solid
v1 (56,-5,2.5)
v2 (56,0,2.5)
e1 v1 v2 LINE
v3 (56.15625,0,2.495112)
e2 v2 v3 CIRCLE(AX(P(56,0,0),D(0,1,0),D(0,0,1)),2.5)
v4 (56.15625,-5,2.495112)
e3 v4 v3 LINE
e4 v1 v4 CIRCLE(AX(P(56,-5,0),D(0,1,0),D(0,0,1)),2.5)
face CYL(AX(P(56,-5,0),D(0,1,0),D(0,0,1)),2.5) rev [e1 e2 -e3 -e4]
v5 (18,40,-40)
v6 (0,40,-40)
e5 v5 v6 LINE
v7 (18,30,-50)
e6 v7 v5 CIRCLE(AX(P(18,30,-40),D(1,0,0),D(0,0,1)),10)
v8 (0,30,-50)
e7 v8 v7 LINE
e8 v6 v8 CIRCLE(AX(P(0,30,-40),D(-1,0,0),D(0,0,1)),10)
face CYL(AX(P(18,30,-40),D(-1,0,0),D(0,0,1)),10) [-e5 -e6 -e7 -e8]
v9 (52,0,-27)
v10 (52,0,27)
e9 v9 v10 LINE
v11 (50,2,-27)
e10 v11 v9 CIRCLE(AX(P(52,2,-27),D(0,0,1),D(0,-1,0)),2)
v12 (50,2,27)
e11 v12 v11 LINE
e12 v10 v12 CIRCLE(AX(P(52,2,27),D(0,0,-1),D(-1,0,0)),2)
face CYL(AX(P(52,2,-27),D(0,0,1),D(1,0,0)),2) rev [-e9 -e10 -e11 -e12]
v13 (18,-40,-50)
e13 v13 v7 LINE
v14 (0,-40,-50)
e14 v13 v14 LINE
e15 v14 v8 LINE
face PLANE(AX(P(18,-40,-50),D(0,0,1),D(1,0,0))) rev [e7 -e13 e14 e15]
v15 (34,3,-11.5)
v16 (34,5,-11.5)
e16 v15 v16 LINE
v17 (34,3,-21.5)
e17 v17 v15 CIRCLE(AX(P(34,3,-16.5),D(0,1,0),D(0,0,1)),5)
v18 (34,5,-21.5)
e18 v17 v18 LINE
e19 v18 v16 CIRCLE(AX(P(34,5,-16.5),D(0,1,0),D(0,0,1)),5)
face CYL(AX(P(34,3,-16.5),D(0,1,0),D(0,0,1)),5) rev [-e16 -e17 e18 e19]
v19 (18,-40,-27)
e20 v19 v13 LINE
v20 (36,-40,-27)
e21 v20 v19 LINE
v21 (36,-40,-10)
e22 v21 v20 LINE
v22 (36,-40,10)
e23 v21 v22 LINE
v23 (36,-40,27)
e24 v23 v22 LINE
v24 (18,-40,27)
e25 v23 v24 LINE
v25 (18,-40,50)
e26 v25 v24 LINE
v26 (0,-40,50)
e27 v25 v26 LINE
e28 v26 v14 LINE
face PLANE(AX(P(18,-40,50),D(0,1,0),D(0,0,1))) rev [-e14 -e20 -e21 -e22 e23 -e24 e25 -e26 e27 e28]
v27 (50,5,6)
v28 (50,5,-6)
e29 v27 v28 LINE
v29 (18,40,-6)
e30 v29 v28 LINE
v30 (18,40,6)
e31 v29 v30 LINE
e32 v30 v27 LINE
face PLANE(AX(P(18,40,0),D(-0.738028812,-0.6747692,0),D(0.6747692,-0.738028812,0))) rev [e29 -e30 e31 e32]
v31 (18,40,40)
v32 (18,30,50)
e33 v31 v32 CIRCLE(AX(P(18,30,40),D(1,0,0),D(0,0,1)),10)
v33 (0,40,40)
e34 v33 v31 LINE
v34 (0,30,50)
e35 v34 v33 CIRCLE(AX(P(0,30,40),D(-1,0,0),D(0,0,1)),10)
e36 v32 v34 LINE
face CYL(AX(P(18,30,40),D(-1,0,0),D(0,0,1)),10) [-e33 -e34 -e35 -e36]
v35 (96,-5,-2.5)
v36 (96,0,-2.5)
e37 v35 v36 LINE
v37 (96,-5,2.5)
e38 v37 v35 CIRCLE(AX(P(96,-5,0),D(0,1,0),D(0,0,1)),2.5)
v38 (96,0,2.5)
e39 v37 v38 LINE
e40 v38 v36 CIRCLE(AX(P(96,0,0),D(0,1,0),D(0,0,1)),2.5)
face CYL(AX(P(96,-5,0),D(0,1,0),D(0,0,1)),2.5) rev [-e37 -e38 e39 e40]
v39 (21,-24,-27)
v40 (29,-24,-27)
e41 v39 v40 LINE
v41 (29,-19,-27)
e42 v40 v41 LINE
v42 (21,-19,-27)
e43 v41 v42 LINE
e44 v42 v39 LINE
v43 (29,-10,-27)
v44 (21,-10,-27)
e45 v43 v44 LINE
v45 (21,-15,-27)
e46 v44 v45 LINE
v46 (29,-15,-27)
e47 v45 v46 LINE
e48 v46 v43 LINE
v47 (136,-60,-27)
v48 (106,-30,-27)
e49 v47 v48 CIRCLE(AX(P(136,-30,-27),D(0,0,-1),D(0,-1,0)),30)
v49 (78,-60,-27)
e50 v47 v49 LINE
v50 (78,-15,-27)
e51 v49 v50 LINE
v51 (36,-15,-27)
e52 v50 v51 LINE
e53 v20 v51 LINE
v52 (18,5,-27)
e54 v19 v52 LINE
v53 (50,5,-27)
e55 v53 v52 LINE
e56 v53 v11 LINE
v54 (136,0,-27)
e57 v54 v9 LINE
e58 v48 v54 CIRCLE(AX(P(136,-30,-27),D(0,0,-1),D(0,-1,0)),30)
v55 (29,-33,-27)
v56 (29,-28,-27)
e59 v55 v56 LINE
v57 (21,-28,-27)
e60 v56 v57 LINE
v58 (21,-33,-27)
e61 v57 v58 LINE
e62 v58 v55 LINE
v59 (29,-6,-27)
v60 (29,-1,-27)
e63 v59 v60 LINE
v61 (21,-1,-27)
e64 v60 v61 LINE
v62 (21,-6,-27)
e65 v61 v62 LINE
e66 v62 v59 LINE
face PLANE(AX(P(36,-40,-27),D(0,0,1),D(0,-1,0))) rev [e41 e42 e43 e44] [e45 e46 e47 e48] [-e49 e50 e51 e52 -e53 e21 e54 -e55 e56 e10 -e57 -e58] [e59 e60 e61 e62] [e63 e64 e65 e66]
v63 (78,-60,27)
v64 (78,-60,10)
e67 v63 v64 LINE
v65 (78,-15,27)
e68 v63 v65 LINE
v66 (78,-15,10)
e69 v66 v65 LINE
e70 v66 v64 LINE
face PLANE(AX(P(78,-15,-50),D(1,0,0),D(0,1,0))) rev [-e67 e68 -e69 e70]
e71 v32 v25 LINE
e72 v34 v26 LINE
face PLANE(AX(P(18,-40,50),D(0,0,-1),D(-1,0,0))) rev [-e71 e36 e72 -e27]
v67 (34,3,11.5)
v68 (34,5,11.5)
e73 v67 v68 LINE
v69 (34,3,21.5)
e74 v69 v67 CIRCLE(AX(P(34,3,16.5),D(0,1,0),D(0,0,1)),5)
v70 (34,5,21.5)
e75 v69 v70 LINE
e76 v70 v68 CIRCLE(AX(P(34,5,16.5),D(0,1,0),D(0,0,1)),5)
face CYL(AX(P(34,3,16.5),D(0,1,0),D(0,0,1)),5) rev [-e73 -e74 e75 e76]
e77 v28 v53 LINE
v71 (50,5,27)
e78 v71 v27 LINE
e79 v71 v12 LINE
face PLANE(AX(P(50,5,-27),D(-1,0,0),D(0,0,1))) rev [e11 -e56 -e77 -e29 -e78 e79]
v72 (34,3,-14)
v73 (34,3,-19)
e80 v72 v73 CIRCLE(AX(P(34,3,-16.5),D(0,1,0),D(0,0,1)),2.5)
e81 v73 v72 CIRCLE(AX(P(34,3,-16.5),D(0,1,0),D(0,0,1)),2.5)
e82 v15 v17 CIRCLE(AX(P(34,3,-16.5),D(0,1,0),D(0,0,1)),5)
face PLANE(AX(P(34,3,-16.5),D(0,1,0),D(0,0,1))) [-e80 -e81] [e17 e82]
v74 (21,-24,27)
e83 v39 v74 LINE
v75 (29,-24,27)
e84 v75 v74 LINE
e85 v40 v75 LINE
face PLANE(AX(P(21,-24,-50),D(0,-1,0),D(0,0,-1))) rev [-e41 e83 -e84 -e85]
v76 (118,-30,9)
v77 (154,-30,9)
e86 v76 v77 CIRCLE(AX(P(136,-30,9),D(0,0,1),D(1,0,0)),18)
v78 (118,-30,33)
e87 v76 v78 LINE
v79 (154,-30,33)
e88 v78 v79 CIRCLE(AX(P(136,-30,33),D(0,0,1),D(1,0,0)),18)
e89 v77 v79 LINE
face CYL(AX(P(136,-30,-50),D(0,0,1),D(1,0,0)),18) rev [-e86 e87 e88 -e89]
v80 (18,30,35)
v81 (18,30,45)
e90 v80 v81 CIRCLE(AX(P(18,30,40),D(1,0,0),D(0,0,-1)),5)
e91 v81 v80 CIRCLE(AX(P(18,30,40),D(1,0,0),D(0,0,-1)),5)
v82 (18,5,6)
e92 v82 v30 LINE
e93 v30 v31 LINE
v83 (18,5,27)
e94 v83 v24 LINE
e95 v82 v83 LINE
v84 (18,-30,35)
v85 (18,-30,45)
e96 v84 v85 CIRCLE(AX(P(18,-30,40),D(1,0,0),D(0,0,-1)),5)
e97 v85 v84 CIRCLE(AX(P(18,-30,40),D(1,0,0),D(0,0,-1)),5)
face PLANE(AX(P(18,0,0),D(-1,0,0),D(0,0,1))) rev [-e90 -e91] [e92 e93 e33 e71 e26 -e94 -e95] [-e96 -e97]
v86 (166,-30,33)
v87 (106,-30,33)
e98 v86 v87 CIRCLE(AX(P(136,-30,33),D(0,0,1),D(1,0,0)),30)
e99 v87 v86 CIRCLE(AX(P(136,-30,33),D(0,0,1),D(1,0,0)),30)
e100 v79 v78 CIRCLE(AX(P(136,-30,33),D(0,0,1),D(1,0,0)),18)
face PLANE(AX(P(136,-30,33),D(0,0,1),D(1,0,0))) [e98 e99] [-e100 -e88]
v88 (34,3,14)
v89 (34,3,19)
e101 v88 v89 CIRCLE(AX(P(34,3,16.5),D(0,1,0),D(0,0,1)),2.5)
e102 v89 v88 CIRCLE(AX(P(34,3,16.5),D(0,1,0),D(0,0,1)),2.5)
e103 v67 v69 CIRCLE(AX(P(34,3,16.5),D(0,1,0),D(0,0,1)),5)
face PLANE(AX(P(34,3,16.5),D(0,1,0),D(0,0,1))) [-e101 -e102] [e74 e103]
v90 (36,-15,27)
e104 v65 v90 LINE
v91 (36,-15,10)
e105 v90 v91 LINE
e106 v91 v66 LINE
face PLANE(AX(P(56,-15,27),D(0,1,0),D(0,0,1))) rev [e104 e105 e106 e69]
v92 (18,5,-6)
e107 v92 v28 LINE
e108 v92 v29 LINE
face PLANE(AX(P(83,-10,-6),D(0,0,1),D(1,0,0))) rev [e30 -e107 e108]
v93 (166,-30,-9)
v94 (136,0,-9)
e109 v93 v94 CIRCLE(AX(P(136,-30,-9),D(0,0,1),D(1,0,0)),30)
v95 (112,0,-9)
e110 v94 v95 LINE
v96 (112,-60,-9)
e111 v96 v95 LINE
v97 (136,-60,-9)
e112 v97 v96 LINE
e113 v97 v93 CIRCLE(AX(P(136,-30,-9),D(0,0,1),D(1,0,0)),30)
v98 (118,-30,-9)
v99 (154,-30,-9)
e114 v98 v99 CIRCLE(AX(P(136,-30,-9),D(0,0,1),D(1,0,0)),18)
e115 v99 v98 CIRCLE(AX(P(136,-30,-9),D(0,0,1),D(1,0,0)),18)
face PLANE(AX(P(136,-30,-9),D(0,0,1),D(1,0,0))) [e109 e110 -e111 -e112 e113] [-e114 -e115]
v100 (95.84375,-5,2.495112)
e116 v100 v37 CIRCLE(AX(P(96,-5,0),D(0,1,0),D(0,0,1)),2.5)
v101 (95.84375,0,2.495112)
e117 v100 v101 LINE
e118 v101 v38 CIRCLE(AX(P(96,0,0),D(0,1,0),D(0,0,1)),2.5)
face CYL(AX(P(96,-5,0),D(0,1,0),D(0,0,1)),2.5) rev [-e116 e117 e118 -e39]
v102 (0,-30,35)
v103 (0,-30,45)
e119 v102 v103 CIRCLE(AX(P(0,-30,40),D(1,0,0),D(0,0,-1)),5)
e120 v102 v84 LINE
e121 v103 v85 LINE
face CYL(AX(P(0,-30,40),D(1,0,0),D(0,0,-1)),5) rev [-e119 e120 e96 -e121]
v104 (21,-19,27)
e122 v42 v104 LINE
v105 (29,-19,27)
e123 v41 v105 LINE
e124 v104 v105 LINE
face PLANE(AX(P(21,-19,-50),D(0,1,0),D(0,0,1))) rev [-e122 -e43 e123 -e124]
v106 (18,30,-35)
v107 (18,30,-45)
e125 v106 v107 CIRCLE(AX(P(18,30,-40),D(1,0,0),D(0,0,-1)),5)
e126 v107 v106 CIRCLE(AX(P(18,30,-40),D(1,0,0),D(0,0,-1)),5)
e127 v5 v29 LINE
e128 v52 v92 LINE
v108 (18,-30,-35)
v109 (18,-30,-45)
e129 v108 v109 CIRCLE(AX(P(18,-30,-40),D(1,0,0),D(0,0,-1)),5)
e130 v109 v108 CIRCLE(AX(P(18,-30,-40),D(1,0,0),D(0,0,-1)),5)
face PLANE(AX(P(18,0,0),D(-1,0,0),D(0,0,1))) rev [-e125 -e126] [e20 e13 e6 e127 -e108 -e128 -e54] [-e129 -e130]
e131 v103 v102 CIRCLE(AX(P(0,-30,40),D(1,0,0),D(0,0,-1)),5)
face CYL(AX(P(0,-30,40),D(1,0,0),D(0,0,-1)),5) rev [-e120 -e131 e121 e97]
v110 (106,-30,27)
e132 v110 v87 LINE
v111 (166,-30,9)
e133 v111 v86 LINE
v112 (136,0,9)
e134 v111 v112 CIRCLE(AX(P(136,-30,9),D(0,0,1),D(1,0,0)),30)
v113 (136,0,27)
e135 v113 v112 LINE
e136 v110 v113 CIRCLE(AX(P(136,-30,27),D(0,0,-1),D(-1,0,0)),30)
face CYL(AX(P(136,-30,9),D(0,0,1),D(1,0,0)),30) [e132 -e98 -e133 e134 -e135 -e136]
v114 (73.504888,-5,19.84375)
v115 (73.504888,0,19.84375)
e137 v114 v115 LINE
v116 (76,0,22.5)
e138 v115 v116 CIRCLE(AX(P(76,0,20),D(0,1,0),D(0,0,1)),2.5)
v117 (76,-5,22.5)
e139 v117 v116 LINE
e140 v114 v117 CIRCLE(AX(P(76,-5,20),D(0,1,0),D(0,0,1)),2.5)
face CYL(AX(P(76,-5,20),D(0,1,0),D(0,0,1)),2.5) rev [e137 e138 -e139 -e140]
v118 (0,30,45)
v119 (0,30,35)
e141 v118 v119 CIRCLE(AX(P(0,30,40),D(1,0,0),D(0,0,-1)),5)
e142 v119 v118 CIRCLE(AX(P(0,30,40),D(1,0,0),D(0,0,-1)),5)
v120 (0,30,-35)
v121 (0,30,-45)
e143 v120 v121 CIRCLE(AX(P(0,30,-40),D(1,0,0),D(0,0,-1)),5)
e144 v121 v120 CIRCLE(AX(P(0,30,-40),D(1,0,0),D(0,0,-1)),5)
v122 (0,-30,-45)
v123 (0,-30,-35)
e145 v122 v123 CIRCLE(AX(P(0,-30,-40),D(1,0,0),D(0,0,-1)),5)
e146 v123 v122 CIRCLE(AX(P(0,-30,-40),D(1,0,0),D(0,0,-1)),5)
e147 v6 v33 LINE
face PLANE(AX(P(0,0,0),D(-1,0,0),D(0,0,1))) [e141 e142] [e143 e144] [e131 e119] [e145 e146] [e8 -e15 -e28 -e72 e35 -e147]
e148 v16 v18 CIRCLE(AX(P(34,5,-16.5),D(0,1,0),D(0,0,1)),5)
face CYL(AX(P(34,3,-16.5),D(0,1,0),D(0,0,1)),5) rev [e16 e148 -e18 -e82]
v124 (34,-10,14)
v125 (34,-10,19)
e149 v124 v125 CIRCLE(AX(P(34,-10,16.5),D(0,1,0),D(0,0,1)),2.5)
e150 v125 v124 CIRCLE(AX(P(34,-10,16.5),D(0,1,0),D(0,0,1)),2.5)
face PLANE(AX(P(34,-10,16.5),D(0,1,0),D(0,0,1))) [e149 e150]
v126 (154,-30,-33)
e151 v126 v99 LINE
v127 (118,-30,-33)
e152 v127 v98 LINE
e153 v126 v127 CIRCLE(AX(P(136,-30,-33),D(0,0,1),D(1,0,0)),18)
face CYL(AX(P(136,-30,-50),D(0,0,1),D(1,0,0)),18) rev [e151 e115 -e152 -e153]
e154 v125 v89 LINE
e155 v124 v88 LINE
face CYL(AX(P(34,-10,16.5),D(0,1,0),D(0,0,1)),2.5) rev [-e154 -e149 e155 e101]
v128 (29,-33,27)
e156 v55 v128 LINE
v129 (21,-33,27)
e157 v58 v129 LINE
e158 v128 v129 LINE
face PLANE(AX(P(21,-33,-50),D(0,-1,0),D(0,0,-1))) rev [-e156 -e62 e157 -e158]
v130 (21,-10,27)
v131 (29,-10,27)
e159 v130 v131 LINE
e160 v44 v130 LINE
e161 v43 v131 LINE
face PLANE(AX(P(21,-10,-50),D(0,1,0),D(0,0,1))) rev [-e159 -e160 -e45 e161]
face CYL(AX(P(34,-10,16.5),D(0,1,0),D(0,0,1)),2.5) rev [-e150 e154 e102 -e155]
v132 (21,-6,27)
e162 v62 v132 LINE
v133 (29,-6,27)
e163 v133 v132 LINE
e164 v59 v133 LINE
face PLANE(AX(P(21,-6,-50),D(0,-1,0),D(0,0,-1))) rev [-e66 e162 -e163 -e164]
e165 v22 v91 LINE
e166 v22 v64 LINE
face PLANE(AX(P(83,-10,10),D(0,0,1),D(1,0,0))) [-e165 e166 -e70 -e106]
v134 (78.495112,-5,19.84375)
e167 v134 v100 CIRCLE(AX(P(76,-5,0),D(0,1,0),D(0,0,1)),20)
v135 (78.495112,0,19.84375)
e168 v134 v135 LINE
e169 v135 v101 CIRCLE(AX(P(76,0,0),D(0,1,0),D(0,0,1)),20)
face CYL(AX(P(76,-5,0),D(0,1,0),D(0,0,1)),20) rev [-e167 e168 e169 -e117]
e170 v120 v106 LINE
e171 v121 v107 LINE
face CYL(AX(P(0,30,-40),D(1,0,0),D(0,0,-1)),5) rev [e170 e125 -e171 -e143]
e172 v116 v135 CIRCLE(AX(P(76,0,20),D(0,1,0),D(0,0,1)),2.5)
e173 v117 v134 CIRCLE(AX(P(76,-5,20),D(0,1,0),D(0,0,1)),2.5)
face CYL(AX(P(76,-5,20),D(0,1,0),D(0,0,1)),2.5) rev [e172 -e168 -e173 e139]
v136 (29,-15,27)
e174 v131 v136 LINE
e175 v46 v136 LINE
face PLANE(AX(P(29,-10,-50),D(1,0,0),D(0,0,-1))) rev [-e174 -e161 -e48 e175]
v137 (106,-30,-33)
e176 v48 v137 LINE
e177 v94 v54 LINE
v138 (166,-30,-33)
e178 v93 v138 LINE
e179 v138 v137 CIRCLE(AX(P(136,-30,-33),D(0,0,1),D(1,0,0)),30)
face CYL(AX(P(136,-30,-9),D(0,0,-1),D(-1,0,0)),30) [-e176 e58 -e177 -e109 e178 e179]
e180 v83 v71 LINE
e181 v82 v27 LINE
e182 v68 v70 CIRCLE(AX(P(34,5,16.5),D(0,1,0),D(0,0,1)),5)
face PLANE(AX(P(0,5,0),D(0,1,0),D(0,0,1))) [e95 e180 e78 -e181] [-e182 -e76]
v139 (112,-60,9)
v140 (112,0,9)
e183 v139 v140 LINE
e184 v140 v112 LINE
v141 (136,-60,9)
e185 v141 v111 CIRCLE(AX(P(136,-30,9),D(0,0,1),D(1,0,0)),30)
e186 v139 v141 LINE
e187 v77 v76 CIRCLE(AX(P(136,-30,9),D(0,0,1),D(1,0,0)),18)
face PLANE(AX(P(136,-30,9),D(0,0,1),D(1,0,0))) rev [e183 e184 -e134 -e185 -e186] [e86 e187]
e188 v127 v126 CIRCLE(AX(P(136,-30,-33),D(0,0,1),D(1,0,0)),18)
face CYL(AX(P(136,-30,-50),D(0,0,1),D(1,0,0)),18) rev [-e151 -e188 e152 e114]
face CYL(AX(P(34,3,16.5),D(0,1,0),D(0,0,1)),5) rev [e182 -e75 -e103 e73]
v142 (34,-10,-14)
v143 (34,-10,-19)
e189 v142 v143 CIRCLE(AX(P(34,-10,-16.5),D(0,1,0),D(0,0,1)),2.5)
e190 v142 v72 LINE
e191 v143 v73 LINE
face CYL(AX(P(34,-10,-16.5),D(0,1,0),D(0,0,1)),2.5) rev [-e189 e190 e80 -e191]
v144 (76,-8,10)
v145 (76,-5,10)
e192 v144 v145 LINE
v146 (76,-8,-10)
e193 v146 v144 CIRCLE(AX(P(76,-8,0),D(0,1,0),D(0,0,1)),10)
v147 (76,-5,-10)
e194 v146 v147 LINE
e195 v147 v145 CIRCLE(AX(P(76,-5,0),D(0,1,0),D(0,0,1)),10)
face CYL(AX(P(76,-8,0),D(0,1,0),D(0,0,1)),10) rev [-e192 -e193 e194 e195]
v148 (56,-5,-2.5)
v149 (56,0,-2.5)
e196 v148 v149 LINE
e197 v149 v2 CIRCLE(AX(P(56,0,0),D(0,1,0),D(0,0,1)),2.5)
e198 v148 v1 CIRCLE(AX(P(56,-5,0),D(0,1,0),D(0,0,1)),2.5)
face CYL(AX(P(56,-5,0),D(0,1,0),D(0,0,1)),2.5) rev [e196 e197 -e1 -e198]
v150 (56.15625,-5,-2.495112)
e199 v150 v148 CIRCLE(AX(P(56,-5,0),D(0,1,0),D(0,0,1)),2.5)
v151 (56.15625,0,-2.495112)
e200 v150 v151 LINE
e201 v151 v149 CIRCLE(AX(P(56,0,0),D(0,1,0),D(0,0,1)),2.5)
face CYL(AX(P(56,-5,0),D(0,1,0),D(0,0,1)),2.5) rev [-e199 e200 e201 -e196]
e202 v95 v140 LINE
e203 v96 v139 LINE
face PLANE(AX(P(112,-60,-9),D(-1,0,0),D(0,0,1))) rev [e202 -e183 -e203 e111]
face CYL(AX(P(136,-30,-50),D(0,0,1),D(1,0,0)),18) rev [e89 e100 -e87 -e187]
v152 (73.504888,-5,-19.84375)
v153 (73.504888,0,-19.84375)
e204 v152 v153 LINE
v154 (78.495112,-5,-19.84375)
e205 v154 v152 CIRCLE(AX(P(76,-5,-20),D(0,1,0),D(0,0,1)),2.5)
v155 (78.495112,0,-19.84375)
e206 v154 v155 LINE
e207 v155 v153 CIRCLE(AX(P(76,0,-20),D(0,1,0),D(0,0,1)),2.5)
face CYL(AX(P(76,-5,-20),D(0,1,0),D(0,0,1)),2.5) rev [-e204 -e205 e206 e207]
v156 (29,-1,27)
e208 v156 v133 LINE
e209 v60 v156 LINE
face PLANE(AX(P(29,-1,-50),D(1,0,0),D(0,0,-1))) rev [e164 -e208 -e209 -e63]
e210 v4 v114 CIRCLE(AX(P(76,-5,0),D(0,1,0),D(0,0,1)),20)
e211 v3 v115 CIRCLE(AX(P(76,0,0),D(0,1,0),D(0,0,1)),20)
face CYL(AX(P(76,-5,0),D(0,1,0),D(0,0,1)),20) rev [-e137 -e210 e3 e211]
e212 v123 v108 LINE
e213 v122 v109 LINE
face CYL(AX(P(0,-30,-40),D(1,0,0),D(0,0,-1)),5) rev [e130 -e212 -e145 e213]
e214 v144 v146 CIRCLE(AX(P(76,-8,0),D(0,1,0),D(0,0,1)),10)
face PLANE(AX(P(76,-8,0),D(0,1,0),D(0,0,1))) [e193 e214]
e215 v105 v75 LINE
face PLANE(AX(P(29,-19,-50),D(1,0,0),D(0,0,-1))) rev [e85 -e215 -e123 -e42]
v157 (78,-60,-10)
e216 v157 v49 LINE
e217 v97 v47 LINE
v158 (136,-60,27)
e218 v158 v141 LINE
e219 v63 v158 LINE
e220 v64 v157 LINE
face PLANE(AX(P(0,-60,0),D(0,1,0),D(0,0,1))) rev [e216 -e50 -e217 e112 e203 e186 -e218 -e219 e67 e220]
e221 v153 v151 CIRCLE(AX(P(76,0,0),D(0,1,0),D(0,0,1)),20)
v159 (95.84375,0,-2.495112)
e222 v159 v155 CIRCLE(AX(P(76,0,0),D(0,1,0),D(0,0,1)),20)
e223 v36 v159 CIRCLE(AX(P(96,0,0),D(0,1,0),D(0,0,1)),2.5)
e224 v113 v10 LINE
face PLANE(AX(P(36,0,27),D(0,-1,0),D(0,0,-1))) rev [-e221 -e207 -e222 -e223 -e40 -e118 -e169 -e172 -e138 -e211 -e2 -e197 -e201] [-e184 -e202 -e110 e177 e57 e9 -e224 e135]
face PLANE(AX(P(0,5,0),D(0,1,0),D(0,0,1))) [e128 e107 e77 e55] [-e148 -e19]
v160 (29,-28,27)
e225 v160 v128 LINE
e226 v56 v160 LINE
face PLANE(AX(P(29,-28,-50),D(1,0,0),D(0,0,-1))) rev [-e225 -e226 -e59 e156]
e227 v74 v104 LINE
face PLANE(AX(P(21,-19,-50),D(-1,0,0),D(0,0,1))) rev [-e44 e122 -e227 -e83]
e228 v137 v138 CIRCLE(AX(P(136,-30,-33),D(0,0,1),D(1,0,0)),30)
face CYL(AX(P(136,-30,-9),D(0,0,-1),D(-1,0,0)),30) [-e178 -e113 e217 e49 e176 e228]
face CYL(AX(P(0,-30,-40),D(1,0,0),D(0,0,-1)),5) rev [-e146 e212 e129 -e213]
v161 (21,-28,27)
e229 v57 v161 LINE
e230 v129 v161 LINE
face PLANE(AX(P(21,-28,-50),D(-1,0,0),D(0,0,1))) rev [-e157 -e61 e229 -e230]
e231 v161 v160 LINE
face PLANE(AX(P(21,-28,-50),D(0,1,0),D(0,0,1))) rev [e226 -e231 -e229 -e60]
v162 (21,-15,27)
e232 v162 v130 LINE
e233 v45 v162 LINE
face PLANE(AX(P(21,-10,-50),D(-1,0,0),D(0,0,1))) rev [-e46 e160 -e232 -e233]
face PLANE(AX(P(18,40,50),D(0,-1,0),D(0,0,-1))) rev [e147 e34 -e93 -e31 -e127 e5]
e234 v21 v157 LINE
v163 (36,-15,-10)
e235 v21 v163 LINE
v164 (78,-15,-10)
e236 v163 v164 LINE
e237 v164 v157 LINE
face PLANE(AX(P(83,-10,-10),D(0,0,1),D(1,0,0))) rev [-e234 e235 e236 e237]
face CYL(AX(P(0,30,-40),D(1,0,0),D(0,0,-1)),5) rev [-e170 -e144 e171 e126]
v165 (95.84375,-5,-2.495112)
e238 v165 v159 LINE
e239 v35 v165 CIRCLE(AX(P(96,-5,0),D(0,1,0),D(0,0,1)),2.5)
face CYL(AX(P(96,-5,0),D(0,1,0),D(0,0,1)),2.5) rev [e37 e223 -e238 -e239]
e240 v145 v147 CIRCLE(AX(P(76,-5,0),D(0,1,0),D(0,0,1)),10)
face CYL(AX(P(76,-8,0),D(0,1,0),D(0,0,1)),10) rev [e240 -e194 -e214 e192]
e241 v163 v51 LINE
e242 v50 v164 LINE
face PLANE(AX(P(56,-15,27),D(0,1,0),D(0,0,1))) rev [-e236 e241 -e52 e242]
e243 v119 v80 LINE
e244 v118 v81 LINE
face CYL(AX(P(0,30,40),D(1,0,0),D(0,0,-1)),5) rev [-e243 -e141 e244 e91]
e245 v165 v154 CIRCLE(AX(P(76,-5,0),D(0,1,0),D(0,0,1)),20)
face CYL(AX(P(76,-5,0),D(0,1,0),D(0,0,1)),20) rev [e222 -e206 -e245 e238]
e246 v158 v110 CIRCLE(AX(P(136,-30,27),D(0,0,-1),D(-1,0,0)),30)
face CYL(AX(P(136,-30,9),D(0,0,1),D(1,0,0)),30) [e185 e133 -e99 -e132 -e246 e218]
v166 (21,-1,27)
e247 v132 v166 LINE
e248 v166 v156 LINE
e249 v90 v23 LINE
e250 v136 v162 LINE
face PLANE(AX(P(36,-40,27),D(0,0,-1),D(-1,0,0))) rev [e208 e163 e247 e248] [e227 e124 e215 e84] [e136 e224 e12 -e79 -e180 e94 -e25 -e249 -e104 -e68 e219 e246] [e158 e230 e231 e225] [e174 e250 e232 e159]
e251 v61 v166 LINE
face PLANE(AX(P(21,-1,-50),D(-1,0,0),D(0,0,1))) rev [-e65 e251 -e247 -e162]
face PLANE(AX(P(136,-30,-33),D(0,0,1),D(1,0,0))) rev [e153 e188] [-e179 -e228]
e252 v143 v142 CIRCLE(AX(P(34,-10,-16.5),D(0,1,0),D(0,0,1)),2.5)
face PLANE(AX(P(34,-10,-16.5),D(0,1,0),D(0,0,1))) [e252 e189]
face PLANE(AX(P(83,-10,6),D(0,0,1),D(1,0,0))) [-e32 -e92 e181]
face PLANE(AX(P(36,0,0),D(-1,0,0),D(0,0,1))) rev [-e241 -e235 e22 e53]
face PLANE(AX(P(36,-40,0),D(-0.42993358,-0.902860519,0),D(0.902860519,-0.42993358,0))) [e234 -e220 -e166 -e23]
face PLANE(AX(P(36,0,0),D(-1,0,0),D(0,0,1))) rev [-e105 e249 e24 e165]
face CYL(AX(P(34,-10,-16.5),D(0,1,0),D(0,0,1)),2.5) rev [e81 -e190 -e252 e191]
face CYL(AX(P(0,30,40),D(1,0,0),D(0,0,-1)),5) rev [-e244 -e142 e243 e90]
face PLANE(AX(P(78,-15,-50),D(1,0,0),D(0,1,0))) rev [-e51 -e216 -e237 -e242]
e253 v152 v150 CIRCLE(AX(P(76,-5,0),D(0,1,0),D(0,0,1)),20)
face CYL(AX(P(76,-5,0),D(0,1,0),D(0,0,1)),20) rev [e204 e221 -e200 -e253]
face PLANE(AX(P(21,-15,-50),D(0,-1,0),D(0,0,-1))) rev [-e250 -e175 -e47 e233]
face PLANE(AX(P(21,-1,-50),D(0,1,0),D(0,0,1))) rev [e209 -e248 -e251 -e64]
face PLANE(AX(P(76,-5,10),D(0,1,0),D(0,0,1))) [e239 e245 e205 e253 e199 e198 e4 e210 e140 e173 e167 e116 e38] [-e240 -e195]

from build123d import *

# Parameters (mm, degrees)
MOUNTING_FLANGE_SKETCH_W          = 100
MOUNTING_FLANGE_SKETCH_H          = 80
MOUNTING_FLANGE_DEPTH             = 18
FLANGE_BOSS_BLOCK_SKETCH_W        = 54
FLANGE_BOSS_BLOCK_SKETCH_H        = 40
FLANGE_BOSS_BLOCK_DEPTH           = 18
ARM_RISER_SKETCH_W                = 54
ARM_RISER_SKETCH_H                = 15
ARM_RISER_DEPTH                   = 20
SUPPORT_ARM_SKETCH_W              = 80
SUPPORT_ARM_SKETCH_H              = 54
SUPPORT_ARM_DEPTH                 = 60
CLEVIS_LUG_1_SKETCH_R             = 30
CLEVIS_LUG_1_DEPTH                = 24
CLEVIS_START                      = 24
CLEVIS_LUG_2_SKETCH_R             = 30
CLEVIS_LUG_2_DEPTH                = 24
CLEVIS_BORE_SKETCH_R              = 18
CLEVIS_BORE_36_DEPTH              = 196.05127531
CLEVIS_SLOT_SKETCH_W              = 24
CLEVIS_SLOT_SKETCH_H              = 18
CLEVIS_SLOT_24_MM_DEPTH           = 184.455716727
ARM_RELIEF_CUT_SKETCH_W           = 22
ARM_RELIEF_CUT_SKETCH_H           = 45
ARM_RELIEF_CUT_DEPTH              = 193.574660846
ARM_RIB_20_MM_REACH               = 185.456
ARM_RIB_SKETCH_WALL_W             = 415.430246854
ARM_RIB_SKETCH_WALL_H             = 20
TOP_PAD_SKETCH_W                  = 32
TOP_PAD_SKETCH_H                  = 54
TOP_PAD_DEPTH                     = 5
TOP_PAD_FILLET_R2_R               = 2
GUSSET_RIB_12_MM_REACH            = 185.456
GUSSET_RIB_SKETCH_WALL_W          = 416.33505626
GUSSET_RIB_SKETCH_WALL_H          = 12
FLANGE_CORNER_FILLETS_R10_R       = 10
FLANGE_MOUNTING_HOLES_SKETCH_R    = 5
FLANGE_MOUNTING_HOLES_4X_DEPTH    = 168.343957166
SIDE_SQUARE_POCKETS_4X_DEPTH      = 193.574660846
SIDE_SQUARE_POCKETS_4X_DEPTH_BACK = 193.574660846
SIDE_SQUARE_POCKETS_SKETCH_W      = 8
SIDE_SQUARE_POCKETS_SKETCH_H      = 5
COUNTERBORE_SKETCH_R              = 5
COUNTERBORES_10_DEPTH             = 2
PILOT_HOLES_SKETCH_R              = 2.5
PILOT_HOLES_5_DEPTH               = 13
ARM_TOP_RECESS_40_DEPTH           = 5
RECESS_CENTRE_POCKET_SKETCH_R     = 10
RECESS_CENTRE_POCKET_20_DEPTH     = 3


with BuildPart() as part:
    # Mounting Flange Sketch → Mounting Flange (new body)
    with BuildSketch(Plane(origin=(0, 0, 0), x_dir=(0, 0, -1), z_dir=(1, 0, 0))):
        Rectangle(MOUNTING_FLANGE_SKETCH_W, MOUNTING_FLANGE_SKETCH_H)
    extrude(amount=MOUNTING_FLANGE_DEPTH)

    # Flange Boss Block Sketch → Flange Boss Block (add)
    with BuildSketch(Plane(origin=(18, 0, 0), x_dir=(0, 0, -1), z_dir=(1, 0, 0))):
        with Locations((0, -20)):
            Rectangle(FLANGE_BOSS_BLOCK_SKETCH_W, FLANGE_BOSS_BLOCK_SKETCH_H)
    extrude(amount=FLANGE_BOSS_BLOCK_DEPTH)

    # Arm Riser Sketch → Arm Riser (add)
    with BuildSketch(Plane(origin=(36, 0, 0), x_dir=(0, 0, -1), z_dir=(1, 0, 0))):
        with Locations((0, -7.5)):
            Rectangle(ARM_RISER_SKETCH_W, ARM_RISER_SKETCH_H)
    extrude(amount=ARM_RISER_DEPTH)

    # Support Arm Sketch → Support Arm (add)
    with BuildSketch(Plane(origin=(0, 0, 0), x_dir=(1, 0, 0), z_dir=(0, 1, 0))):
        with Locations((96, 0)):
            Rectangle(SUPPORT_ARM_SKETCH_W, SUPPORT_ARM_SKETCH_H)
    extrude(amount=-SUPPORT_ARM_DEPTH)

    # Clevis Lug 1 Sketch → Clevis Lug 1 (add)
    with BuildSketch(Plane.XY.offset(33)):
        with Locations((136, -30)):
            Circle(CLEVIS_LUG_1_SKETCH_R)
    extrude(amount=-CLEVIS_LUG_1_DEPTH)

    # Clevis Lug 2 Sketch → Clevis Lug 2 (add)
    with BuildSketch(Plane.XY.offset(-33).offset(CLEVIS_START)):
        with Locations((136, -30)):
            Circle(CLEVIS_LUG_2_SKETCH_R)
    extrude(amount=-CLEVIS_LUG_2_DEPTH)

    # Clevis Bore Sketch → Clevis Bore Ø36 (cut, through all)
    with BuildSketch(Plane.XY.offset(33)):
        with Locations((136, -30)):
            Circle(CLEVIS_BORE_SKETCH_R)
    extrude(amount=-CLEVIS_BORE_36_DEPTH, mode=Mode.SUBTRACT)

    # Clevis Slot Sketch → Clevis Slot 24 mm (cut, through all)
    with BuildSketch(Plane(origin=(0, 0, 0), x_dir=(1, 0, 0), z_dir=(0, 1, 0))):
        with Locations((124, 0)):
            Rectangle(CLEVIS_SLOT_SKETCH_W, CLEVIS_SLOT_SKETCH_H)
    extrude(amount=-CLEVIS_SLOT_24_MM_DEPTH, mode=Mode.SUBTRACT)

    # Arm Relief Cut Sketch → Arm Relief Cut (cut, through all)
    with BuildSketch(Plane.XY.offset(27)):
        with Locations((67, -37.5)):
            Rectangle(ARM_RELIEF_CUT_SKETCH_W, ARM_RELIEF_CUT_SKETCH_H)
    extrude(amount=-ARM_RELIEF_CUT_DEPTH, mode=Mode.SUBTRACT)

    # Arm Rib Sketch wall → Arm Rib 20 mm (add, up to next)
    with BuildSketch(Plane(origin=(57, -50, 0), x_dir=(0.902860518824, -0.429933580392, 0), z_dir=(0.429933580392, 0.902860518824, 0)), mode=Mode.PRIVATE) as arm_rib_20_mm_sk1:
        Rectangle(ARM_RIB_SKETCH_WALL_W, ARM_RIB_SKETCH_WALL_H)
    arm_rib_20_mm_tool1 = extrude(arm_rib_20_mm_sk1.sketch, amount=ARM_RIB_20_MM_REACH, mode=Mode.PRIVATE) - part.part
    add(arm_rib_20_mm_tool1.solids().sort_by_distance((57, -50, 0))[0])

    # Top Pad Sketch → Top Pad (add)
    with BuildSketch(Plane(origin=(0, 0, 0), x_dir=(1, 0, 0), z_dir=(0, 1, 0))):
        with Locations((34, 0)):
            Rectangle(TOP_PAD_SKETCH_W, TOP_PAD_SKETCH_H)
    extrude(amount=TOP_PAD_DEPTH)

    # Top Pad Fillet R2
    top_pad_fillet_r2_edges = [part.edges().sort_by_distance(p)[0] for p in [
        (50, 0, 0),
    ]]
    fillet(top_pad_fillet_r2_edges, radius=TOP_PAD_FILLET_R2_R)

    # Gusset Rib Sketch wall → Gusset Rib 12 mm (add, up to next)
    with BuildSketch(Plane(origin=(34, 22.5, 0), x_dir=(0.674769199545, -0.738028812002, 0), z_dir=(0.738028812002, 0.674769199545, 0)), mode=Mode.PRIVATE) as gusset_rib_12_mm_sk1:
        Rectangle(GUSSET_RIB_SKETCH_WALL_W, GUSSET_RIB_SKETCH_WALL_H)
    gusset_rib_12_mm_tool1 = extrude(gusset_rib_12_mm_sk1.sketch, amount=-GUSSET_RIB_12_MM_REACH, mode=Mode.PRIVATE) - part.part
    add(gusset_rib_12_mm_tool1.solids().sort_by_distance((34, 22.5, 0))[0])

    # Flange Corner Fillets R10
    flange_corner_fillets_r10_edges = [part.edges().sort_by_distance(p)[0] for p in [
        (9, 40, 50),
        (9, 40, -50),
    ]]
    fillet(flange_corner_fillets_r10_edges, radius=FLANGE_CORNER_FILLETS_R10_R)

    # Flange Mounting Holes Sketch → Flange Mounting Holes 4x (cut, through all)
    with BuildSketch(Plane(origin=(18, 0, 0), x_dir=(0, 0, -1), z_dir=(1, 0, 0))):
        with Locations((-40, 30)):
            Circle(FLANGE_MOUNTING_HOLES_SKETCH_R)
        with Locations((40, 30)):
            Circle(FLANGE_MOUNTING_HOLES_SKETCH_R)
        with Locations((-40, -30)):
            Circle(FLANGE_MOUNTING_HOLES_SKETCH_R)
        with Locations((40, -30)):
            Circle(FLANGE_MOUNTING_HOLES_SKETCH_R)
    extrude(amount=-FLANGE_MOUNTING_HOLES_4X_DEPTH, mode=Mode.SUBTRACT)

    # Side Square Pockets Sketch → Side Square Pockets 4x (cut, two sides: drawn at the far end of the back side and taken through both)
    with BuildSketch(Plane.XY.offset(27).offset(-SIDE_SQUARE_POCKETS_4X_DEPTH_BACK)):
        with Locations((25, -3.5)):
            Rectangle(SIDE_SQUARE_POCKETS_SKETCH_W, SIDE_SQUARE_POCKETS_SKETCH_H)
        with Locations((25, -12.5)):
            Rectangle(SIDE_SQUARE_POCKETS_SKETCH_W, SIDE_SQUARE_POCKETS_SKETCH_H)
        with Locations((25, -21.5)):
            Rectangle(SIDE_SQUARE_POCKETS_SKETCH_W, SIDE_SQUARE_POCKETS_SKETCH_H)
        with Locations((25, -30.5)):
            Rectangle(SIDE_SQUARE_POCKETS_SKETCH_W, SIDE_SQUARE_POCKETS_SKETCH_H)
    extrude(amount=SIDE_SQUARE_POCKETS_4X_DEPTH + SIDE_SQUARE_POCKETS_4X_DEPTH_BACK, mode=Mode.SUBTRACT)

    # Counterbore Sketch → Counterbores Ø10 (cut)
    with BuildSketch(Plane(origin=(0, 5, 0), x_dir=(1, 0, 0), z_dir=(0, 1, 0))):
        with Locations(Location((34, -16.5, 0), (0, 0, 270))):
            Circle(COUNTERBORE_SKETCH_R)
        with Locations(Location((34, 16.5, 0), (0, 0, 270))):
            Circle(COUNTERBORE_SKETCH_R)
    extrude(amount=-COUNTERBORES_10_DEPTH, mode=Mode.SUBTRACT)

    # Pilot Holes Sketch → Pilot Holes Ø5 (cut)
    with BuildSketch(Plane(origin=(0, 3, 0), x_dir=(1, 0, 0), z_dir=(0, 1, 0))):
        with Locations(Location((34, 16.5, 0), (0, 0, 270))):
            Circle(PILOT_HOLES_SKETCH_R)
        with Locations(Location((34, -16.5, 0), (0, 0, 270))):
            Circle(PILOT_HOLES_SKETCH_R)
    extrude(amount=-PILOT_HOLES_5_DEPTH, mode=Mode.SUBTRACT)

    # Arm Top Recess Sketch → Arm Top Recess Ø40 (cut)
    with BuildSketch(Plane(origin=(0, 0, 0), x_dir=(1, 0, 0), z_dir=(0, 1, 0))):
        with BuildLine():
            ThreePointArc((73.50488759, 19.84375), (61.857864376, 14.142135624), (56.15625, 2.49511241))
            ThreePointArc((56.15625, 2.49511241), (53.5, 0), (56.15625, -2.49511241))
            ThreePointArc((56.15625, -2.49511241), (61.857864376, -14.142135624), (73.50488759, -19.84375))
            ThreePointArc((73.50488759, -19.84375), (76, -22.5), (78.49511241, -19.84375))
            ThreePointArc((78.49511241, -19.84375), (90.142135624, -14.142135624), (95.84375, -2.49511241))
            ThreePointArc((95.84375, -2.49511241), (98.5, 0), (95.84375, 2.49511241))
            ThreePointArc((95.84375, 2.49511241), (90.142135624, 14.142135624), (78.49511241, 19.84375))
            ThreePointArc((78.49511241, 19.84375), (76, 22.5), (73.50488759, 19.84375))
        make_face()
    extrude(amount=-ARM_TOP_RECESS_40_DEPTH, mode=Mode.SUBTRACT)

    # Recess Centre Pocket Sketch → Recess Centre Pocket Ø20 (cut)
    with BuildSketch(Plane(origin=(0, -5, 0), x_dir=(1, 0, 0), z_dir=(0, 1, 0))):
        with Locations(Location((76, 0, 0), (0, 0, 270))):
            Circle(RECESS_CENTRE_POCKET_SKETCH_R)
    extrude(amount=-RECESS_CENTRE_POCKET_20_DEPTH, mode=Mode.SUBTRACT)


solid = part.part
